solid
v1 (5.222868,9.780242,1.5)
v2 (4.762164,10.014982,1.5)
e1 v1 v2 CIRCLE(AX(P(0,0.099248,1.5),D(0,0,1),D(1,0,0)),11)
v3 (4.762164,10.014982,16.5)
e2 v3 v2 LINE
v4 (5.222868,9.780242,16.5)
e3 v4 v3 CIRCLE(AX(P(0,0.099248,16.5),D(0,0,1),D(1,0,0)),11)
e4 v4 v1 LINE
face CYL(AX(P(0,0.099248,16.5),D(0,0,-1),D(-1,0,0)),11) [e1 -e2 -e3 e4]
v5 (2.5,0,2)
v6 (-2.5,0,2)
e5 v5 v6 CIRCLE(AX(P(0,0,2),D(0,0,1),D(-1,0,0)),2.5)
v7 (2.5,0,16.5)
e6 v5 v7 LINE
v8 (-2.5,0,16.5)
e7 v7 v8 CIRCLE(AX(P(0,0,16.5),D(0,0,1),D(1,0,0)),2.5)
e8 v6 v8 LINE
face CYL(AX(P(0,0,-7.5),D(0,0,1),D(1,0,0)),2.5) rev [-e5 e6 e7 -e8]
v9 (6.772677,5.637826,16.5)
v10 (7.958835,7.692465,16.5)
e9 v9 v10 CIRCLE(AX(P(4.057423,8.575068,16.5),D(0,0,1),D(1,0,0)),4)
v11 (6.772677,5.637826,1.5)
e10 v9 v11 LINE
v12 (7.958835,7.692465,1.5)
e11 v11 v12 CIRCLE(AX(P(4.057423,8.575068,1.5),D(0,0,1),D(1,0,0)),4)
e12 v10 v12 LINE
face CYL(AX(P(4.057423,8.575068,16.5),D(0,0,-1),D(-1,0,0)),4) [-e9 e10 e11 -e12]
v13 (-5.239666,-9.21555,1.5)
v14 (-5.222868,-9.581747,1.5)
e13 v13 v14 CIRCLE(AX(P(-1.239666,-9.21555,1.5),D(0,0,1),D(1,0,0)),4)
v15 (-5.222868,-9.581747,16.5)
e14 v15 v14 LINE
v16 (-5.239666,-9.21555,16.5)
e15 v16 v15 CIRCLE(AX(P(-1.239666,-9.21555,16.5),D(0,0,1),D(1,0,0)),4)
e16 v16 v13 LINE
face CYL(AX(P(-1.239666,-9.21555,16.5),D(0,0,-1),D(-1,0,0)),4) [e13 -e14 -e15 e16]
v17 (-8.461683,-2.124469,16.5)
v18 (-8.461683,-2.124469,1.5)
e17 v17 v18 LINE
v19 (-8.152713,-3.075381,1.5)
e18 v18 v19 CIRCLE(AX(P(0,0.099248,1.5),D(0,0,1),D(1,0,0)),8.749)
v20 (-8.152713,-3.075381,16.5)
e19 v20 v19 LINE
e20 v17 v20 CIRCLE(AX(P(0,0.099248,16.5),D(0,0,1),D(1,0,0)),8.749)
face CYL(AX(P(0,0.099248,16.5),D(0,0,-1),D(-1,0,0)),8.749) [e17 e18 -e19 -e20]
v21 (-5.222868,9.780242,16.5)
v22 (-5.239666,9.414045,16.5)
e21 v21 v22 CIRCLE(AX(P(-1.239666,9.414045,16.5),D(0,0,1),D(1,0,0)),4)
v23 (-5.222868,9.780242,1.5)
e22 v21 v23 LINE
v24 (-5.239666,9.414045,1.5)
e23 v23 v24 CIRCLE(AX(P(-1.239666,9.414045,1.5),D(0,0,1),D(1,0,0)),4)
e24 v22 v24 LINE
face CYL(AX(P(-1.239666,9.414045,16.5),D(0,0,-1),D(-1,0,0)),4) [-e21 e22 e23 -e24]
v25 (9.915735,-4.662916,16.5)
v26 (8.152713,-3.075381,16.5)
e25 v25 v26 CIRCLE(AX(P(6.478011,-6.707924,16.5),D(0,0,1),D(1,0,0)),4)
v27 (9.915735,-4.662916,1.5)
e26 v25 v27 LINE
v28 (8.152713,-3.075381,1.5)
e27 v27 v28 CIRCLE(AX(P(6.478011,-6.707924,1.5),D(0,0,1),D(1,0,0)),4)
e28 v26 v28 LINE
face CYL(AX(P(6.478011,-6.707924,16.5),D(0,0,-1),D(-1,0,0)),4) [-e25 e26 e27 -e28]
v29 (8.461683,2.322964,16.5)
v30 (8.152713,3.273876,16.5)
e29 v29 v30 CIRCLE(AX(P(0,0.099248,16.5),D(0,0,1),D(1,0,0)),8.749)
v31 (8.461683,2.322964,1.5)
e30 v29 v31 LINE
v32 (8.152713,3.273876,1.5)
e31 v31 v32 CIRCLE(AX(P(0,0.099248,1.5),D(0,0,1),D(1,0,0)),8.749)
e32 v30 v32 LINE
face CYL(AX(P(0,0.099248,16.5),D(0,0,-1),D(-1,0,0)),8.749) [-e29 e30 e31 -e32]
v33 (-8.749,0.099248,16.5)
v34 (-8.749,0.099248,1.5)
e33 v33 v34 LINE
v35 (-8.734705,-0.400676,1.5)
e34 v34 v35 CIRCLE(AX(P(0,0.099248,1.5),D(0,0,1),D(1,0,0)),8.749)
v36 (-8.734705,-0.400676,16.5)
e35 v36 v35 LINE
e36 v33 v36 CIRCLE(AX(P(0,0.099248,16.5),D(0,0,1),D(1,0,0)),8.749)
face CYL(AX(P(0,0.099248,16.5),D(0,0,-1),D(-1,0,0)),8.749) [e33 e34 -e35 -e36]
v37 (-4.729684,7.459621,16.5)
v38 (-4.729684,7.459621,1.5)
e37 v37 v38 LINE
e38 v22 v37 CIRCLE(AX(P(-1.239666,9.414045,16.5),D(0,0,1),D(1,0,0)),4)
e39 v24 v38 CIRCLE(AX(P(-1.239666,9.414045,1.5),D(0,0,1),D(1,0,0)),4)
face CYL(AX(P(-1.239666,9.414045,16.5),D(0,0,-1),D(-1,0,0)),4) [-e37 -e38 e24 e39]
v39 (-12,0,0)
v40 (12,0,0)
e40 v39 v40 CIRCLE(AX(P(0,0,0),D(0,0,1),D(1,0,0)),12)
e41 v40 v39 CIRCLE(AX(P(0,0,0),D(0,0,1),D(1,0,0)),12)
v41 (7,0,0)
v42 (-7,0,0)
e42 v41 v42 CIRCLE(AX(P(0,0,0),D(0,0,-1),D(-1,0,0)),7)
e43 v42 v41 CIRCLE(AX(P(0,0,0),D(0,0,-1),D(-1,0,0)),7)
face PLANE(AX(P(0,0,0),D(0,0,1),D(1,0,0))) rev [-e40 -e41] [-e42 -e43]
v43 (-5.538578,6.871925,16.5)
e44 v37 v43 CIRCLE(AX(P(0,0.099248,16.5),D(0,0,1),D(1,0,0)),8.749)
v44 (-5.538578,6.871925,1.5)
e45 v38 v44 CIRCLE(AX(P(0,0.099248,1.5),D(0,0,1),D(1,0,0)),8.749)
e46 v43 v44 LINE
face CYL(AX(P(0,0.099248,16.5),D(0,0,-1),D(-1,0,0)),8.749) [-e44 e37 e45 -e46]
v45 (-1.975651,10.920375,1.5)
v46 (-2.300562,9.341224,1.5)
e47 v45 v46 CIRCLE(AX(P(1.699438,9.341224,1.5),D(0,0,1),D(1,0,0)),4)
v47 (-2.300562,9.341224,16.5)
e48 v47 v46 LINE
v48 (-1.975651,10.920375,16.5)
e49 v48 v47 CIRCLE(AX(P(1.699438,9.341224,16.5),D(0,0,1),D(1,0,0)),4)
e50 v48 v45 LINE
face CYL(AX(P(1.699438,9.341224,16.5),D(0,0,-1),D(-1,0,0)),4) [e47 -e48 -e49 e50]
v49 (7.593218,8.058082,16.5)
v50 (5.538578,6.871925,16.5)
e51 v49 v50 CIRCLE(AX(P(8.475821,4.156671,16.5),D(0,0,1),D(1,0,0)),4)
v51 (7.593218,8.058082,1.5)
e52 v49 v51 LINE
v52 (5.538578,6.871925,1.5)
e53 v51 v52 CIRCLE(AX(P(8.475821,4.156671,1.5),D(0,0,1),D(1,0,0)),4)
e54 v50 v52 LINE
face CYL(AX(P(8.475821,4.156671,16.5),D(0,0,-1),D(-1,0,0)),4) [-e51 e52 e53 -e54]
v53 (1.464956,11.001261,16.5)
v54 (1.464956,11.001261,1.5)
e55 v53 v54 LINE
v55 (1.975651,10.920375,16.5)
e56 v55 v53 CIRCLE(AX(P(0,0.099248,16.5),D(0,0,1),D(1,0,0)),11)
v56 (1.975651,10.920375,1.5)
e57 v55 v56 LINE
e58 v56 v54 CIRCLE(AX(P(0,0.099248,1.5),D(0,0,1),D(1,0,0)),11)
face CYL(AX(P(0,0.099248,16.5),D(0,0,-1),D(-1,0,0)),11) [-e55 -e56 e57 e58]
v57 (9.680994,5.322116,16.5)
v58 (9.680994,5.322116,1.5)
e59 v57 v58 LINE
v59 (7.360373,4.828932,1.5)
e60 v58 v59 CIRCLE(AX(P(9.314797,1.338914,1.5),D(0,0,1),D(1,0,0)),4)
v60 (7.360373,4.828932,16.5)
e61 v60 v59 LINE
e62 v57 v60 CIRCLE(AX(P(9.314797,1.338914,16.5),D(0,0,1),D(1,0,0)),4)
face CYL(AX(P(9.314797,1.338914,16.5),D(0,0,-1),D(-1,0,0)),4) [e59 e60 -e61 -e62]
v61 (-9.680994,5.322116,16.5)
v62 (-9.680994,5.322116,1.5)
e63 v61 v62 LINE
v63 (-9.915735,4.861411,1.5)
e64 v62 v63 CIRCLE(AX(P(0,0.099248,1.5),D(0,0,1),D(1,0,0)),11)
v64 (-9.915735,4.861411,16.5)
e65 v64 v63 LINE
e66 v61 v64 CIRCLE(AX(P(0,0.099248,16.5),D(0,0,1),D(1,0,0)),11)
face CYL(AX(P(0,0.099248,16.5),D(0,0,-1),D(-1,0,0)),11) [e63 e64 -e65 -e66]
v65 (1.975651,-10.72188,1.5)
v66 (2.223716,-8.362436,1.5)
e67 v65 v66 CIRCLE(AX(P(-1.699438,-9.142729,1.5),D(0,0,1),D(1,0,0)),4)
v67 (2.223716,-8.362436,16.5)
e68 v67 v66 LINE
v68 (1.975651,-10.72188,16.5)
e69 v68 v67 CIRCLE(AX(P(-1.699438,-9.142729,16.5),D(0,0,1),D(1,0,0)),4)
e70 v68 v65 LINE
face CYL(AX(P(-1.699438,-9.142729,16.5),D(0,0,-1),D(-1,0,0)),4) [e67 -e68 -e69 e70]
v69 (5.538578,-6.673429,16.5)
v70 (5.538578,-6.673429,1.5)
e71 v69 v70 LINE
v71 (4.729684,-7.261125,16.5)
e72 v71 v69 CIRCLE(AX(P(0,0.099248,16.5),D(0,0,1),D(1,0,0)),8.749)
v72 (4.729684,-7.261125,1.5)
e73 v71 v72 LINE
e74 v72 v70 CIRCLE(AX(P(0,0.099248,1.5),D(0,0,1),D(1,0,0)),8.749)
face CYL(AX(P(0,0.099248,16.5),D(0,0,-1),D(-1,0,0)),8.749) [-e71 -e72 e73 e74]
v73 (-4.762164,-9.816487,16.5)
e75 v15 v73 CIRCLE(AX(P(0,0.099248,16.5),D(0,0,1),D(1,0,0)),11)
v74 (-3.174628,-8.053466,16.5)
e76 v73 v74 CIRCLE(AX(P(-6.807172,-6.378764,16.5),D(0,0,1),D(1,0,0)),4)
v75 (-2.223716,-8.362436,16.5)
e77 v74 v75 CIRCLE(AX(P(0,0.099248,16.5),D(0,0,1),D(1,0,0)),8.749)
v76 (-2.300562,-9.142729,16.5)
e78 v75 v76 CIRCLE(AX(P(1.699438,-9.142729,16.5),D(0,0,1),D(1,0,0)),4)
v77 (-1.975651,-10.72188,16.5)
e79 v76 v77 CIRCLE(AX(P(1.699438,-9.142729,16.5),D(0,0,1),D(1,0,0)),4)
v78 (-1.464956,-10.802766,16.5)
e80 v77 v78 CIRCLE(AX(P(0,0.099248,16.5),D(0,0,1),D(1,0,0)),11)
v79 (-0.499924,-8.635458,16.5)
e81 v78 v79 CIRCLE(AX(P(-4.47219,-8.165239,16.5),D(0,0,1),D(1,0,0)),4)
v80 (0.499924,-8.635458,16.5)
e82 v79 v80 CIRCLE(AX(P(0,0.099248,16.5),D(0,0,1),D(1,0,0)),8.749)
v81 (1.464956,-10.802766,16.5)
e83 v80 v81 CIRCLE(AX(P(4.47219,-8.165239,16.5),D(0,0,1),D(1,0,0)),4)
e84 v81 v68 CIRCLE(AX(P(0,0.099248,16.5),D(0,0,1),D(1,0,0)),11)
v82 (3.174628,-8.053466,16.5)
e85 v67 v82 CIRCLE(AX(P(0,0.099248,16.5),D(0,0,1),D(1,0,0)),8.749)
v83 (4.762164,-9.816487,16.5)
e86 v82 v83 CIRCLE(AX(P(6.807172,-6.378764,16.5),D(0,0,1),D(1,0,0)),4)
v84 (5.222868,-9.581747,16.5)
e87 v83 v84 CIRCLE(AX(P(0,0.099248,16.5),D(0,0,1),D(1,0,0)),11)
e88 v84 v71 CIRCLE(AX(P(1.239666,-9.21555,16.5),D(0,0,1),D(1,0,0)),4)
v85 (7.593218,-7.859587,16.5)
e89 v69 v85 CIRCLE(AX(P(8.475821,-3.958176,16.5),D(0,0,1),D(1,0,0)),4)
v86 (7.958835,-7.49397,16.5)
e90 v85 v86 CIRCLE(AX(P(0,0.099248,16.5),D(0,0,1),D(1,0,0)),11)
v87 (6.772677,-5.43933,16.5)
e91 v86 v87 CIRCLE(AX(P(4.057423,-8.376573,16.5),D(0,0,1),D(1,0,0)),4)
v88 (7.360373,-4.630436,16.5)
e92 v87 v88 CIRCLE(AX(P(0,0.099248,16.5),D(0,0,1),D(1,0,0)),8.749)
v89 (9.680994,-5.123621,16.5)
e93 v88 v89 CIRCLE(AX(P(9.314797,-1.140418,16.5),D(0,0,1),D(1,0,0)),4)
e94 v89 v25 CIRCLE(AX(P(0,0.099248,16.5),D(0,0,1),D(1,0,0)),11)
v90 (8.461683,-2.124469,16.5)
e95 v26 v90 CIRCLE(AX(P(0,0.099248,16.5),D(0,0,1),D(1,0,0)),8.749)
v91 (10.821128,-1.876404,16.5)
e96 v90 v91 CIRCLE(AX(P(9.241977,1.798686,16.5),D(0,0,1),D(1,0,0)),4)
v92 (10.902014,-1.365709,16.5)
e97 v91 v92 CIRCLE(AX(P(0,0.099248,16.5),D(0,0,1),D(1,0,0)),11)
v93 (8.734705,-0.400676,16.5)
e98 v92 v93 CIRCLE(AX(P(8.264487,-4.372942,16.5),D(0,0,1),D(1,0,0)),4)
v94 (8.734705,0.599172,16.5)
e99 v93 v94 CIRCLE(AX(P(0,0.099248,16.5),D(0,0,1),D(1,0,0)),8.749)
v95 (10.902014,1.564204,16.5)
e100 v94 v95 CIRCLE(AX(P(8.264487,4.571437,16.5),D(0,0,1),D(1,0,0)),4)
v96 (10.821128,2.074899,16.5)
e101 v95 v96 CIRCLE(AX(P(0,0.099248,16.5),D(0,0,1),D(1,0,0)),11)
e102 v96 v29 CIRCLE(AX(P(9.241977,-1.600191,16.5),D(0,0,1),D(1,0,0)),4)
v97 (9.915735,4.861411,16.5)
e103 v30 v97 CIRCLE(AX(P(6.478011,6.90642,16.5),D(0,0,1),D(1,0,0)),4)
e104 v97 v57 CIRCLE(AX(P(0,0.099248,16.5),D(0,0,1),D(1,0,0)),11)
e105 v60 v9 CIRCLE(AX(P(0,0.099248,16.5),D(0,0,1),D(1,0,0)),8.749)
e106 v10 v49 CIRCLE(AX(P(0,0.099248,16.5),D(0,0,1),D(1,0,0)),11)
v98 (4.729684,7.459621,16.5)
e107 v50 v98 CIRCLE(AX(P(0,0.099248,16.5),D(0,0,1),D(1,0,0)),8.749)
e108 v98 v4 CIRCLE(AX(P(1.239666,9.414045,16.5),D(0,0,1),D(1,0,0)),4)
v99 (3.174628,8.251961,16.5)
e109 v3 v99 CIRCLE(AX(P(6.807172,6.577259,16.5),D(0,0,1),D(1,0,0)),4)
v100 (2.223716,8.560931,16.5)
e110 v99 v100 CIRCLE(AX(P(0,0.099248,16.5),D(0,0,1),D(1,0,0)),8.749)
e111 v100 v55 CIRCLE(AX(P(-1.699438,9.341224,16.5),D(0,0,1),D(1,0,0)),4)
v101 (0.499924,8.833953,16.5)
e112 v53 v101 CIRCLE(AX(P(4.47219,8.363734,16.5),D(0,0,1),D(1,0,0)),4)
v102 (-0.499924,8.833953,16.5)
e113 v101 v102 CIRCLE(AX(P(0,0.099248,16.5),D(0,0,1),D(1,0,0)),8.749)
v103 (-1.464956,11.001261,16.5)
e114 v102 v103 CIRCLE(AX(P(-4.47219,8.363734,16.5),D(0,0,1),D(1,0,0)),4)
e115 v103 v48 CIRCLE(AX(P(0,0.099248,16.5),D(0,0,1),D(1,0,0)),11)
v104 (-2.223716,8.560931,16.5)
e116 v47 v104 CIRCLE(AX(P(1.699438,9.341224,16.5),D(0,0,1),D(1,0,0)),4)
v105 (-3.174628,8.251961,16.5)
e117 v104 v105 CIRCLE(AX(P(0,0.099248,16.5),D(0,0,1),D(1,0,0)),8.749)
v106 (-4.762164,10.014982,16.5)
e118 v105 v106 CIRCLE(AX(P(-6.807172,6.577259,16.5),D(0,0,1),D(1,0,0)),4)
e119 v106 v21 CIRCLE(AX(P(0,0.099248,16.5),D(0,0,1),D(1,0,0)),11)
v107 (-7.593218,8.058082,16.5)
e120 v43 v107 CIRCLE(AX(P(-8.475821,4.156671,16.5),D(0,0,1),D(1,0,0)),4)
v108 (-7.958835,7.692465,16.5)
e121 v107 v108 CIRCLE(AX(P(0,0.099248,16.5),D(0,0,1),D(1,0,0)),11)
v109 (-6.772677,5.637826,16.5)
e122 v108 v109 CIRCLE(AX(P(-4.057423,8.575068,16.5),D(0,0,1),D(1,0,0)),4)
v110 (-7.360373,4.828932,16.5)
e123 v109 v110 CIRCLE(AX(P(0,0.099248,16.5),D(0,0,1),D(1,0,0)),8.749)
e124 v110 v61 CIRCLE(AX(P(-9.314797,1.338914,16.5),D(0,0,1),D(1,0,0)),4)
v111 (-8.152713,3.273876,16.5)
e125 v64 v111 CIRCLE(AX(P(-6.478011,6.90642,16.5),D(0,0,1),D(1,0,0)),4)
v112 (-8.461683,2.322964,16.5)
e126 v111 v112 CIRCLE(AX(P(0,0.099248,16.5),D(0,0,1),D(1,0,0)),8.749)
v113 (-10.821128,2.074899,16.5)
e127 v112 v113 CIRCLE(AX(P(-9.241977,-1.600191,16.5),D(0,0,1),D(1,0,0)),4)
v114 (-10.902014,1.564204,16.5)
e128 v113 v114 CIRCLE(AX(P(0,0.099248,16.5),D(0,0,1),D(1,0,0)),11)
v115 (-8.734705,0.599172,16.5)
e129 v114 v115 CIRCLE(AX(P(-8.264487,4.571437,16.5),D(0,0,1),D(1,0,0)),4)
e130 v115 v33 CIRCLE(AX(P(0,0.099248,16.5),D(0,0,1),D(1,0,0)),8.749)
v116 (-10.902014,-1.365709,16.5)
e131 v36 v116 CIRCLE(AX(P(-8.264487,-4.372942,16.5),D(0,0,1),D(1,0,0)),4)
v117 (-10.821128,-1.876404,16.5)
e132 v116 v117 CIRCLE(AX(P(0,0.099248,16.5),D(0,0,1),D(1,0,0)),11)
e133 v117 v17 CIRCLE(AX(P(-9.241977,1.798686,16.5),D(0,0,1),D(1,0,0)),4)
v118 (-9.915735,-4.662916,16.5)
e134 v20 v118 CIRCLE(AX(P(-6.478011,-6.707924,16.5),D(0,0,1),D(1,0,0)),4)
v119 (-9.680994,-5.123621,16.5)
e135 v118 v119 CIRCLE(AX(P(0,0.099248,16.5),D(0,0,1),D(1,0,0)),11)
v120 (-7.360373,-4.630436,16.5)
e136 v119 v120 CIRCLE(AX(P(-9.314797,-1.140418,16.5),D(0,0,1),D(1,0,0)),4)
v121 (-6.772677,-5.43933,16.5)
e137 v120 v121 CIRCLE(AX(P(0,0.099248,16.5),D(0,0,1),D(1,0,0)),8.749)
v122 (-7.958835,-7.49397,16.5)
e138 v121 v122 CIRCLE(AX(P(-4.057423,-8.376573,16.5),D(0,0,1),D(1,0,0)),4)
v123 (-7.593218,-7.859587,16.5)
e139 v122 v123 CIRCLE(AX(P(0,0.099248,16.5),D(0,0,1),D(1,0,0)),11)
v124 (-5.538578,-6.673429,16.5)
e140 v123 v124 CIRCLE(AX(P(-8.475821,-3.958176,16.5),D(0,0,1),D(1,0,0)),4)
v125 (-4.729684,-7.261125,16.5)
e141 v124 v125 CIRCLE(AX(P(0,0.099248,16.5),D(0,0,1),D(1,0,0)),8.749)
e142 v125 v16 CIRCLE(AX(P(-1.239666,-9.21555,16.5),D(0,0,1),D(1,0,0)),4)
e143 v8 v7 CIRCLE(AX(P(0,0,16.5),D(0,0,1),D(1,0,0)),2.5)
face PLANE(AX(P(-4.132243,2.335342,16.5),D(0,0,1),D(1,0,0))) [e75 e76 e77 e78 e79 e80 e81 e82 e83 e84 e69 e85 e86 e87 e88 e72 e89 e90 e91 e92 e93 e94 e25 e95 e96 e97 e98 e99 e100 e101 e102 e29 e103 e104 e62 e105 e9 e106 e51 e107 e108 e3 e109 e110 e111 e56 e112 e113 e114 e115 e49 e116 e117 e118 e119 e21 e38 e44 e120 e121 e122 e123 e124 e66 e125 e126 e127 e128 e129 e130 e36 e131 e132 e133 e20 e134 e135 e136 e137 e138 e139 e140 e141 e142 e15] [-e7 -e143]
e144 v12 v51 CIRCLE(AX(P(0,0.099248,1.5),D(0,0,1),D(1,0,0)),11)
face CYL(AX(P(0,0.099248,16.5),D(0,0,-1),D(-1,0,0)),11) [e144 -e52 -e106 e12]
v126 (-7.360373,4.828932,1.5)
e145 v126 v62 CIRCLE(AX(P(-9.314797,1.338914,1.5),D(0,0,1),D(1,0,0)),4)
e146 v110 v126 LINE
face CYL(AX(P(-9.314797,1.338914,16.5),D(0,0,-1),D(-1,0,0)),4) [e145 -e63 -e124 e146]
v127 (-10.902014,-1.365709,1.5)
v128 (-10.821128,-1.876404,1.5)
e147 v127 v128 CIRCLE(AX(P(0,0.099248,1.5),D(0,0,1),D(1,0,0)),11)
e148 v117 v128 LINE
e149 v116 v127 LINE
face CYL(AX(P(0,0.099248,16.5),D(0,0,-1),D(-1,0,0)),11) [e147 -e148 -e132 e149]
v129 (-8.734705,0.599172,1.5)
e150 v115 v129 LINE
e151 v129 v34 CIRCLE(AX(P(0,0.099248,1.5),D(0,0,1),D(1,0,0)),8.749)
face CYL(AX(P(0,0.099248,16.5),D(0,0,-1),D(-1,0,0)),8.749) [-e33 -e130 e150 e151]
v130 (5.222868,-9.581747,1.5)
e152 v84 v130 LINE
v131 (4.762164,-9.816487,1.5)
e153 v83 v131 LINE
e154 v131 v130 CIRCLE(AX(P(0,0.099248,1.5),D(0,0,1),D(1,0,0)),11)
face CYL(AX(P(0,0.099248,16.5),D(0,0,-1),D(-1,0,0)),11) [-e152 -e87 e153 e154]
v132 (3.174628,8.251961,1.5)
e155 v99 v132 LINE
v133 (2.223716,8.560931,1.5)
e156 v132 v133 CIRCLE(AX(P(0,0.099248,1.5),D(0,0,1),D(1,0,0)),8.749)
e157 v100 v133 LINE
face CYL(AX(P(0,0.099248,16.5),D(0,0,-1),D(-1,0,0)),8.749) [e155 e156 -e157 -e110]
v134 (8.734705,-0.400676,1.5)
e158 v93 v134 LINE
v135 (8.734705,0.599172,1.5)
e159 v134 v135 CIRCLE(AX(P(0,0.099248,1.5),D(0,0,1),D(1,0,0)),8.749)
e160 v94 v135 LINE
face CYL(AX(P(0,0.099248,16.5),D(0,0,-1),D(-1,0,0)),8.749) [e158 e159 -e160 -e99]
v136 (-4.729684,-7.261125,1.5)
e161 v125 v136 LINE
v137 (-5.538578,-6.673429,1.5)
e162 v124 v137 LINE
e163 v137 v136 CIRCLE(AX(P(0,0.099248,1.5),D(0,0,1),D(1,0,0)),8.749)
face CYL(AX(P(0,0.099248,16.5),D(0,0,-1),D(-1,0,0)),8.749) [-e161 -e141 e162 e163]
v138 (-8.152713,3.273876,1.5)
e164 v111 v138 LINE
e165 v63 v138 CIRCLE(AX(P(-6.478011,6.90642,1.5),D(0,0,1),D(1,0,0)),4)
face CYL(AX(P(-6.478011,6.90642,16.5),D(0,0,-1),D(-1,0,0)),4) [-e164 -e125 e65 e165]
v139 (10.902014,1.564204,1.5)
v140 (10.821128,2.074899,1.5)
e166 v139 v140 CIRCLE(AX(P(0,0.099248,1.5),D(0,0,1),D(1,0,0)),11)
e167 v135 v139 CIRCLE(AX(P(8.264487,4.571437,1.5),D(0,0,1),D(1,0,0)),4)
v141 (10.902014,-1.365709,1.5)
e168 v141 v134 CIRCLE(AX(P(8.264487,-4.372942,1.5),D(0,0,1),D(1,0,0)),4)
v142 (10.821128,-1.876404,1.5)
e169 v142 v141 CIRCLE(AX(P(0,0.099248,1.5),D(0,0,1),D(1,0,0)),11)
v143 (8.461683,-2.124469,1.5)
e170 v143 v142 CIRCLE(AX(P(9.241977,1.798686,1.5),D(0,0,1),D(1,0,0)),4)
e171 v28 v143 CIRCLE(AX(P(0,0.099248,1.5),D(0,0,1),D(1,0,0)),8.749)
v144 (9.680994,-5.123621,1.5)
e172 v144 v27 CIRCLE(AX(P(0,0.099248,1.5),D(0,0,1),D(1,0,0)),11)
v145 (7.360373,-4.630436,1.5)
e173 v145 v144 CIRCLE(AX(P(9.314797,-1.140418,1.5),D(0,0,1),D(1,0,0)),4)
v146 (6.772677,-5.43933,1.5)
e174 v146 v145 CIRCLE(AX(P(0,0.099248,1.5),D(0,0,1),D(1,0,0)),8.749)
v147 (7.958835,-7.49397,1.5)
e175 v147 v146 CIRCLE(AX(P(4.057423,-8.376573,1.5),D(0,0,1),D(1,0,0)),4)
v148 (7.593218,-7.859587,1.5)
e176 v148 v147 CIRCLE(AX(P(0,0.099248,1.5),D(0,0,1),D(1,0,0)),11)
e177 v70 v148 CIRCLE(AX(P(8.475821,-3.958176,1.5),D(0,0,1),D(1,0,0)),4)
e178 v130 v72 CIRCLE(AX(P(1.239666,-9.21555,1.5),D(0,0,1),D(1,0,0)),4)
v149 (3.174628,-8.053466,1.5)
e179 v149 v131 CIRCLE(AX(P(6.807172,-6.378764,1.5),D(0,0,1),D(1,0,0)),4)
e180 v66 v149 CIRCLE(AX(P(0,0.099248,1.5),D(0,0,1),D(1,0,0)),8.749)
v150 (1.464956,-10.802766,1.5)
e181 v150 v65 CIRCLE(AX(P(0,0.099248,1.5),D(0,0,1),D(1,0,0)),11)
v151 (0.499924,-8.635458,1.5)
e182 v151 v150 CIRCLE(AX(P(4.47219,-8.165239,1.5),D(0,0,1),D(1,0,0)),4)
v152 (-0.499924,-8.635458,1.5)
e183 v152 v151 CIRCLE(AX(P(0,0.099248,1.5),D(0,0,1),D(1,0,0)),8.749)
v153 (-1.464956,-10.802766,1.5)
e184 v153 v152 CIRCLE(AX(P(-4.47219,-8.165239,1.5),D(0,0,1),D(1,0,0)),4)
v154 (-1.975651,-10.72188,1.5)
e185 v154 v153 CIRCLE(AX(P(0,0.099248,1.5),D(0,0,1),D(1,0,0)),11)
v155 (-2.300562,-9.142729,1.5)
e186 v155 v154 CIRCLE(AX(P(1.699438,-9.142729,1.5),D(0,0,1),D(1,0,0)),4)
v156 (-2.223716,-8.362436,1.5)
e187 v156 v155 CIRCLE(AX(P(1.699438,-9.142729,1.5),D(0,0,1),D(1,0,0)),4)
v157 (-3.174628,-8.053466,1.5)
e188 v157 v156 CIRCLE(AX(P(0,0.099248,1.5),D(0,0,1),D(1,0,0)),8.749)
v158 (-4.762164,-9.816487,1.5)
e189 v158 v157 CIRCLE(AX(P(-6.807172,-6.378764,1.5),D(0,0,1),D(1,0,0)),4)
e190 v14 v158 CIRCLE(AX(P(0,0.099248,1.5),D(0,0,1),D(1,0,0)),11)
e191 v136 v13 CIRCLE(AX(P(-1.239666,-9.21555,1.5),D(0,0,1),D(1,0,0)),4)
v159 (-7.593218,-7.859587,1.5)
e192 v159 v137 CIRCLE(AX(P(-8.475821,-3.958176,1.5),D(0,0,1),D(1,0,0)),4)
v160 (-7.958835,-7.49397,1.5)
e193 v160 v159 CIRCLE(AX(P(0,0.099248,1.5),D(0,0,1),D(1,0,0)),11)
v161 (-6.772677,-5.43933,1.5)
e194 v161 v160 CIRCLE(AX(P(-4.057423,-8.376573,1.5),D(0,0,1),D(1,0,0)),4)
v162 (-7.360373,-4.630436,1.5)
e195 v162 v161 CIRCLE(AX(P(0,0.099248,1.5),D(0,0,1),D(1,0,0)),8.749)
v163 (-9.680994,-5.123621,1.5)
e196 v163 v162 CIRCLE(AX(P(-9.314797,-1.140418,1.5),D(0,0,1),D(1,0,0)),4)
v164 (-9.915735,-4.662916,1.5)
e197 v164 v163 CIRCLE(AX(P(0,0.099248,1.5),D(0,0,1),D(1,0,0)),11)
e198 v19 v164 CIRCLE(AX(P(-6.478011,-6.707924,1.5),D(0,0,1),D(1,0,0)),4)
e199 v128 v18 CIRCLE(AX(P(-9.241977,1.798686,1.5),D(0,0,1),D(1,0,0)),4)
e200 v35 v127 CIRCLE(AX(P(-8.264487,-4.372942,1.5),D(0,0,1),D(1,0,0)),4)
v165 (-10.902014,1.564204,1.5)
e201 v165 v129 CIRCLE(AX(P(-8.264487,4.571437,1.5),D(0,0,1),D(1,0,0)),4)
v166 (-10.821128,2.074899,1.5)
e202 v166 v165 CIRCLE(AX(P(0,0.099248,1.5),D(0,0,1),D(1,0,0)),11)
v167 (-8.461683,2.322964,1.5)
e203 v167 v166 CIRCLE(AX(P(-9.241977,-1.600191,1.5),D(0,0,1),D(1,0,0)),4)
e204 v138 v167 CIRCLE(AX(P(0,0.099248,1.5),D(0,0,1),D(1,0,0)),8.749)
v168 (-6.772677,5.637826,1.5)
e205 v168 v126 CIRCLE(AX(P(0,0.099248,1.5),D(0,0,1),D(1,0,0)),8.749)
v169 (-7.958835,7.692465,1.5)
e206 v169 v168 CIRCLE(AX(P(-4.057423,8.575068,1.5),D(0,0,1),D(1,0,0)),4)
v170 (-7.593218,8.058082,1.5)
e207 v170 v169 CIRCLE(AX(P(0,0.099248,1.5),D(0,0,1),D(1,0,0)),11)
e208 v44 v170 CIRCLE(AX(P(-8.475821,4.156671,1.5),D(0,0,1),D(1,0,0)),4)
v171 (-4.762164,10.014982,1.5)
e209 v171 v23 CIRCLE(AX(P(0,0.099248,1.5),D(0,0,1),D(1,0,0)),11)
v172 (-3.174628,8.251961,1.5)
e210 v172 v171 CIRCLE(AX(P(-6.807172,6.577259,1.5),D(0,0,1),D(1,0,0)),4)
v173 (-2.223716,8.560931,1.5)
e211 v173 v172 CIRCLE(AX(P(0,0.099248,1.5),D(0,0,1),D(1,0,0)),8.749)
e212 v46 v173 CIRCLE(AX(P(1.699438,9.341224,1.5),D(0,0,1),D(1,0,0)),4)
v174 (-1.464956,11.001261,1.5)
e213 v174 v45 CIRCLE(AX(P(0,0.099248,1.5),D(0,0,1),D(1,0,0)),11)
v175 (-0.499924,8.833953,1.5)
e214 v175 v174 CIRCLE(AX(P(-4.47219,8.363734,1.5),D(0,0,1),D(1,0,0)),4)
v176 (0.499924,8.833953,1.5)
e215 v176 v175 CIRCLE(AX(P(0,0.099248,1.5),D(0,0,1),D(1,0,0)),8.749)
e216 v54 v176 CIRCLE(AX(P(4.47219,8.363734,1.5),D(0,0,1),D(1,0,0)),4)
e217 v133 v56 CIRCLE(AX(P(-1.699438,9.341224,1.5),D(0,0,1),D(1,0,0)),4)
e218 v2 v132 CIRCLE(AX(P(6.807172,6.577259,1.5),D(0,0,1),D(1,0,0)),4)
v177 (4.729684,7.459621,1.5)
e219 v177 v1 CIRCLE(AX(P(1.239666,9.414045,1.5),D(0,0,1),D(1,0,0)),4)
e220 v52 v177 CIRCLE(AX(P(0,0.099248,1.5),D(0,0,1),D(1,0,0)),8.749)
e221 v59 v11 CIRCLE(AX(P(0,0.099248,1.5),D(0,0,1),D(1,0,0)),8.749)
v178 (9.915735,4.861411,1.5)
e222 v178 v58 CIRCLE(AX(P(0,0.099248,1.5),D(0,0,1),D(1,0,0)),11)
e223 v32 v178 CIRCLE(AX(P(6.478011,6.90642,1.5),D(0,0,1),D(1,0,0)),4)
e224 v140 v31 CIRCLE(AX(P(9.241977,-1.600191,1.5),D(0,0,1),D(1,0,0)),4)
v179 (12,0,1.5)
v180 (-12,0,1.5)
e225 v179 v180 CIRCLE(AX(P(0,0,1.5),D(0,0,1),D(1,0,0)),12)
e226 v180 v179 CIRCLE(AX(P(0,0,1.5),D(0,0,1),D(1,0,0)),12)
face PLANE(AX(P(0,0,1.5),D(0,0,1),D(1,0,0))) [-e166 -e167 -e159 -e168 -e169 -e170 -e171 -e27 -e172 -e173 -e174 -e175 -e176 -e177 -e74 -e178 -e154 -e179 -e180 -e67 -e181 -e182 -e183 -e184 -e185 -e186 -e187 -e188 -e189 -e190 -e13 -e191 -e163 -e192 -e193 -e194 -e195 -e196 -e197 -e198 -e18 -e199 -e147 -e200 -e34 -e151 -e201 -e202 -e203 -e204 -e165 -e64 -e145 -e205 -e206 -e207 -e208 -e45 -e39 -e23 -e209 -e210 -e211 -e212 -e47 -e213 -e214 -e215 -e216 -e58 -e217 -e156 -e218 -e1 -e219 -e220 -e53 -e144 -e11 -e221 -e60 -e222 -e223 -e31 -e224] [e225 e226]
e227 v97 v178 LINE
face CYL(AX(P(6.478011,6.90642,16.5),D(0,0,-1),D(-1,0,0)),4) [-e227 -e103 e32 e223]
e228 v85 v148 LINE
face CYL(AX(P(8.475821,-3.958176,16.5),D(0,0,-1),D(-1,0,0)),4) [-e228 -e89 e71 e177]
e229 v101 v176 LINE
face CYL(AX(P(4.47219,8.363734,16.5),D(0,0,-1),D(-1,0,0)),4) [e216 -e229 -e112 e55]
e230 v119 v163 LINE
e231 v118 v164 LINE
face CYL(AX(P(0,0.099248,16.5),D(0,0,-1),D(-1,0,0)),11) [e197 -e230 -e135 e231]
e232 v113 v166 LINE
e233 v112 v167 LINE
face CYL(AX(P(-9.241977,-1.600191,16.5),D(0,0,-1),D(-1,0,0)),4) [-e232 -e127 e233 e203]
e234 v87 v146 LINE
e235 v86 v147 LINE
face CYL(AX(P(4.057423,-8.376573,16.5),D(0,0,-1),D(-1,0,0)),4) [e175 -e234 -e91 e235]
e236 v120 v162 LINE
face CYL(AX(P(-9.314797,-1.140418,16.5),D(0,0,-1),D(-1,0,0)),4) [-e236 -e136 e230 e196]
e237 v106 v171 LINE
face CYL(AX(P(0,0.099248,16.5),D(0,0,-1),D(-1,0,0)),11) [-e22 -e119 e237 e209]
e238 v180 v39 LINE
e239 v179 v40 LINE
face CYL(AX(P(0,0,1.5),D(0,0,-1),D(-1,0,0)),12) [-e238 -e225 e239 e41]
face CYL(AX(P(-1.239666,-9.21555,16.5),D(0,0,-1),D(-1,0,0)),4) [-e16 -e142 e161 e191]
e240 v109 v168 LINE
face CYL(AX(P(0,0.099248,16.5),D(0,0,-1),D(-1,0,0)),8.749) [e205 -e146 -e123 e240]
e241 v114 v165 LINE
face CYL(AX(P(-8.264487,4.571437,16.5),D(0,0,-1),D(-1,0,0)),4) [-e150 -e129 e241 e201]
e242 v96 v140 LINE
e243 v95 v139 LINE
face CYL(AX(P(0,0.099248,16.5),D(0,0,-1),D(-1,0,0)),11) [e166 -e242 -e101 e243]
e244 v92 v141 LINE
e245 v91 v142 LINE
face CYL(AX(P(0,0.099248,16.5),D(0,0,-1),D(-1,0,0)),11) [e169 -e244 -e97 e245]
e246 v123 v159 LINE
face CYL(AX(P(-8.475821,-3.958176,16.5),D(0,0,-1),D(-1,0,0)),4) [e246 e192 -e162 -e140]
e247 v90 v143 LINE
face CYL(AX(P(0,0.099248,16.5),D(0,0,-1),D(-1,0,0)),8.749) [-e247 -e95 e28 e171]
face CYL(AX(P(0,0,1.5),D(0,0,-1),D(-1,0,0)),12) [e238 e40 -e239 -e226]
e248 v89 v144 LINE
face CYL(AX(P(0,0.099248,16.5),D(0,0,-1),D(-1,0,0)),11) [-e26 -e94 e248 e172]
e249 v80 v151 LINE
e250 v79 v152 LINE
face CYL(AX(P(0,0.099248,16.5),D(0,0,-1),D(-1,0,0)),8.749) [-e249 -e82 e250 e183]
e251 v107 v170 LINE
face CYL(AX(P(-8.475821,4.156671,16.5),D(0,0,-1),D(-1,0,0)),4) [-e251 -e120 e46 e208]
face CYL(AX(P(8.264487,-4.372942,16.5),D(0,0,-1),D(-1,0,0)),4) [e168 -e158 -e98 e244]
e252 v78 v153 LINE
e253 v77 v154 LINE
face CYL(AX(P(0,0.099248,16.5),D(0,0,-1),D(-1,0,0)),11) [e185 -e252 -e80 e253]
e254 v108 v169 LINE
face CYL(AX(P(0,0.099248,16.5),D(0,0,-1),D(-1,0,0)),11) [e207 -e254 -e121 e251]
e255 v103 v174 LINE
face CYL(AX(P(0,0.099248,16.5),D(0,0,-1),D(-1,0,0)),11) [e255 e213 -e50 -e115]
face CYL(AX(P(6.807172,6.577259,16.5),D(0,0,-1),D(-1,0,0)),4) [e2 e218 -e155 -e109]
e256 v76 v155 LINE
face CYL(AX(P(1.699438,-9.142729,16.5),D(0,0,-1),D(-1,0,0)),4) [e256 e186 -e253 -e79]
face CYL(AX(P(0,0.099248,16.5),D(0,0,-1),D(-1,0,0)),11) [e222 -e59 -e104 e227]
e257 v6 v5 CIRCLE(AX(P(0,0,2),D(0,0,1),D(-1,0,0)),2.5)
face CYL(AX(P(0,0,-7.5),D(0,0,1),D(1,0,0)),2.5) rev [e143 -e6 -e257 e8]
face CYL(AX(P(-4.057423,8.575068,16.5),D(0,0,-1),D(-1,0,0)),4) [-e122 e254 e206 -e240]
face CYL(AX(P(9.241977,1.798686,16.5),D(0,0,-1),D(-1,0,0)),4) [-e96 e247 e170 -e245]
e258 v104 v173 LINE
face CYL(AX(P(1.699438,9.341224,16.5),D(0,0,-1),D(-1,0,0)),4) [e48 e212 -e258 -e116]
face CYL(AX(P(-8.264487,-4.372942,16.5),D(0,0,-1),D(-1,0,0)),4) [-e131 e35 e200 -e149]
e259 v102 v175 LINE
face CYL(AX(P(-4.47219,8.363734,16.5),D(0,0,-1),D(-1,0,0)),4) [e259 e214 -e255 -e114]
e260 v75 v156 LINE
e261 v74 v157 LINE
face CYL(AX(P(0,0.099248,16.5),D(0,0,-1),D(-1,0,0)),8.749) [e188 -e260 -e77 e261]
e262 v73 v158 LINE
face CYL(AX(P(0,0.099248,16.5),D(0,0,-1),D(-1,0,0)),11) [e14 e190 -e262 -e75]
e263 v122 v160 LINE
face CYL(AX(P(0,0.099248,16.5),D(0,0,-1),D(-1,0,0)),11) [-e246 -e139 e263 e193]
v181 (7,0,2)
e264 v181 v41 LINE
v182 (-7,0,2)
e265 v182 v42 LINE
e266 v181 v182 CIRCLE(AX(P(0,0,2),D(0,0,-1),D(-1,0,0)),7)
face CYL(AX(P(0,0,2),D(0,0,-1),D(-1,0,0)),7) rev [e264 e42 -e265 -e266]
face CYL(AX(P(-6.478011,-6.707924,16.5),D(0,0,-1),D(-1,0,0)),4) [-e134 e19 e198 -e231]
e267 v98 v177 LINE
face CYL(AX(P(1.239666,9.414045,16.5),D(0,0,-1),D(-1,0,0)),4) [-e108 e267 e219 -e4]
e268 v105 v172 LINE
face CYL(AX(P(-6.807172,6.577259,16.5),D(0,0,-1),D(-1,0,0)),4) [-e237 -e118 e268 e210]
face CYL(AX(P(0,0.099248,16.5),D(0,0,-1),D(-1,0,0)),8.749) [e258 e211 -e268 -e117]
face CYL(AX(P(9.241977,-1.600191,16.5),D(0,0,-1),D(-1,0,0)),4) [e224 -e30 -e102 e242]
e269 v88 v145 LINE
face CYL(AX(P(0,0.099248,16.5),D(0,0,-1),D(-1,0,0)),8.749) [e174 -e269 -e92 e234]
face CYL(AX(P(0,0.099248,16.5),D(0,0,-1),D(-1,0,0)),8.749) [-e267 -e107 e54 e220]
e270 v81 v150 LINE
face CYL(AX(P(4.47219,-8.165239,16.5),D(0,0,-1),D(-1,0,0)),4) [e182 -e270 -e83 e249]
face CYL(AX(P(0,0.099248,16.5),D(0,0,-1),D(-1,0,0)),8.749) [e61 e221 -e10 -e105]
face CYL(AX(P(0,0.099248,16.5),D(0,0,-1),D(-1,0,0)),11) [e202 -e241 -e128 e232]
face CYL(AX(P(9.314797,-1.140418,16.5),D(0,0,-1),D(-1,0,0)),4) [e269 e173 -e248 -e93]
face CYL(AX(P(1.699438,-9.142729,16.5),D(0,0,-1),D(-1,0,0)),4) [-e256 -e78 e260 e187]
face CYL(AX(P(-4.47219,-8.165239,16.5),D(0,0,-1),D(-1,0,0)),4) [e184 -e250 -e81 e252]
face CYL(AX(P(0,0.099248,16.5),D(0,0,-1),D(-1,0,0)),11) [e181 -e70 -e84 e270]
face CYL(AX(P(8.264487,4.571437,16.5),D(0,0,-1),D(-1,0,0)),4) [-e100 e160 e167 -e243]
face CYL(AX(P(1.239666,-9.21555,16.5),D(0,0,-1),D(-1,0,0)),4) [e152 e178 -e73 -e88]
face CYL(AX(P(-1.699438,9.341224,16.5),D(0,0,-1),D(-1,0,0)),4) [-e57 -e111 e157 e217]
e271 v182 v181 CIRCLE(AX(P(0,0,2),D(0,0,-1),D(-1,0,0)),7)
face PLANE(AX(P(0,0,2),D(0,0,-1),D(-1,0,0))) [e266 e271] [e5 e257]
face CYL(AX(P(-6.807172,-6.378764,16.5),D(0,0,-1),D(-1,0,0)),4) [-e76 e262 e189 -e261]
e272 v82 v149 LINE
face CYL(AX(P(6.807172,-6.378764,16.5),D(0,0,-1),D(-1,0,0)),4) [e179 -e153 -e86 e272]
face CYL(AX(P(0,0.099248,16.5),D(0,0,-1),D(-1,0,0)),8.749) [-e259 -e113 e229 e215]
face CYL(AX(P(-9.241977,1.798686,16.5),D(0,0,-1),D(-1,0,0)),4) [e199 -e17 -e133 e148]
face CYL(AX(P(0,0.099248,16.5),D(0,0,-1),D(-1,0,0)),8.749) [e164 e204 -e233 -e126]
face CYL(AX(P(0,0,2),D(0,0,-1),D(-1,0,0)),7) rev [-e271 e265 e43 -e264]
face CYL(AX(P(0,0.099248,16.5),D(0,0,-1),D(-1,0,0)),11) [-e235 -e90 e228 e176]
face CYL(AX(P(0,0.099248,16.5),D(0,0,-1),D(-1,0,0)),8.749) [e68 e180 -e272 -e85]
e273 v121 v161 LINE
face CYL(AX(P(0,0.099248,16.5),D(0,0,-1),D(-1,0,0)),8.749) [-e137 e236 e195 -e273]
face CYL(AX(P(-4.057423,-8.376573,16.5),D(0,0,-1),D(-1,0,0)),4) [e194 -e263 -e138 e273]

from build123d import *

# Parameters (mm, degrees)
SKETCH1_R           = 12
BOSS_EXTRUDE1_DEPTH = 1.5
BOSS_EXTRUDE2_DEPTH = 15
SKETCH3_R           = 2.5
CUT_EXTRUDE1_DEPTH  = 24
SKETCH4_R           = 7
CUT_EXTRUDE2_DEPTH  = 2


with BuildPart() as part:
    # Sketch1 → Boss-Extrude1 (new body)
    with BuildSketch(Plane.XY):
        Circle(SKETCH1_R)
    extrude(amount=BOSS_EXTRUDE1_DEPTH)

    # Sketch2 → Boss-Extrude2 (add)
    with BuildSketch(Plane.XY.offset(1.5)):
        with BuildLine():
            ThreePointArc((-10.902013697, 1.564204022), (-9.891552344, 0.917308412), (-8.734705318, 0.599171595))
            ThreePointArc((-8.734705318, 0.599171595), (-8.749, 0.099247587), (-8.734705318, -0.40067642))
            ThreePointArc((-8.734705318, -0.40067642), (-9.891552344, -0.718813238), (-10.902013697, -1.365708848))
            ThreePointArc((-10.902013697, -1.365708848), (-10.864571747, -1.621531528), (-10.821127601, -1.876403554))
            ThreePointArc((-10.821127601, -1.876403554), (-9.66022001, -2.179388109), (-8.461683425, -2.124468812))
            ThreePointArc((-8.461683425, -2.124468812), (-8.320793461, -2.604342097), (-8.152713396, -3.075380782))
            ThreePointArc((-8.152713396, -3.075380782), (-9.154630615, -3.735432266), (-9.915734733, -4.662916282))
            ThreePointArc((-9.915734733, -4.662916282), (-9.801071766, -4.89464791), (-9.680994141, -5.123620632))
            ThreePointArc((-9.680994141, -5.123620632), (-8.483278035, -5.053035893), (-7.360373002, -4.630436364))
            ThreePointArc((-7.360373002, -4.630436364), (-7.078089684, -5.043285585), (-6.772677084, -5.4393304))
            ThreePointArc((-6.772677084, -5.4393304), (-7.521589858, -6.376686112), (-7.958834566, -7.493969936))
            ThreePointArc((-7.958834566, -7.493969936), (-7.778174593, -7.678927006), (-7.593217523, -7.859586978))
            ThreePointArc((-7.593217523, -7.859586978), (-6.4759337, -7.422342271), (-5.538577987, -6.673429497))
            ThreePointArc((-5.538577987, -6.673429497), (-5.142533172, -6.978842097), (-4.729683951, -7.261125414))
            ThreePointArc((-4.729683951, -7.261125414), (-5.15228348, -8.384030448), (-5.222868219, -9.581746554))
            ThreePointArc((-5.222868219, -9.581746554), (-4.993895497, -9.701824179), (-4.762163869, -9.816487145))
            ThreePointArc((-4.762163869, -9.816487145), (-3.834679853, -9.055383028), (-3.174628369, -8.053465809))
            ThreePointArc((-3.174628369, -8.053465809), (-2.703589684, -8.221545874), (-2.223716399, -8.362435837))
            ThreePointArc((-2.223716399, -8.362435837), (-2.278635697, -9.560972423), (-1.975651141, -10.721880014))
            ThreePointArc((-1.975651141, -10.721880014), (-1.720779115, -10.765324159), (-1.464956435, -10.802766109))
            ThreePointArc((-1.464956435, -10.802766109), (-0.818060825, -9.792304756), (-0.499924007, -8.63545773))
            ThreePointArc((-0.499924007, -8.63545773), (0, -8.649752413), (0.499924007, -8.63545773))
            ThreePointArc((0.499924007, -8.63545773), (0.818060825, -9.792304756), (1.464956435, -10.802766109))
            ThreePointArc((1.464956435, -10.802766109), (1.720779115, -10.765324159), (1.975651141, -10.721880014))
            ThreePointArc((1.975651141, -10.721880014), (2.278635697, -9.560972423), (2.223716399, -8.362435837))
            ThreePointArc((2.223716399, -8.362435837), (2.703589684, -8.221545874), (3.174628369, -8.053465809))
            ThreePointArc((3.174628369, -8.053465809), (3.834679853, -9.055383028), (4.762163869, -9.816487145))
            ThreePointArc((4.762163869, -9.816487145), (4.993895497, -9.701824179), (5.222868219, -9.581746554))
            ThreePointArc((5.222868219, -9.581746554), (5.15228348, -8.384030448), (4.729683951, -7.261125414))
            ThreePointArc((4.729683951, -7.261125414), (5.142533172, -6.978842097), (5.538577987, -6.673429497))
            ThreePointArc((5.538577987, -6.673429497), (6.4759337, -7.422342271), (7.593217523, -7.859586978))
            ThreePointArc((7.593217523, -7.859586978), (7.778174593, -7.678927006), (7.958834566, -7.493969936))
            ThreePointArc((7.958834566, -7.493969936), (7.521589858, -6.376686112), (6.772677084, -5.4393304))
            ThreePointArc((6.772677084, -5.4393304), (7.078089684, -5.043285585), (7.360373002, -4.630436364))
            ThreePointArc((7.360373002, -4.630436364), (8.483278035, -5.053035893), (9.680994141, -5.123620632))
            ThreePointArc((9.680994141, -5.123620632), (9.801071766, -4.89464791), (9.915734733, -4.662916282))
            ThreePointArc((9.915734733, -4.662916282), (9.154630615, -3.735432266), (8.152713396, -3.075380782))
            ThreePointArc((8.152713396, -3.075380782), (8.320793461, -2.604342097), (8.461683425, -2.124468812))
            ThreePointArc((8.461683425, -2.124468812), (9.66022001, -2.179388109), (10.821127601, -1.876403554))
            ThreePointArc((10.821127601, -1.876403554), (10.864571747, -1.621531528), (10.902013697, -1.365708848))
            ThreePointArc((10.902013697, -1.365708848), (9.891552344, -0.718813238), (8.734705318, -0.40067642))
            ThreePointArc((8.734705318, -0.40067642), (8.749, 0.099247587), (8.734705318, 0.599171595))
            ThreePointArc((8.734705318, 0.599171595), (9.891552344, 0.917308412), (10.902013697, 1.564204022))
            ThreePointArc((10.902013697, 1.564204022), (10.864571747, 1.820026703), (10.821127601, 2.074898729))
            ThreePointArc((10.821127601, 2.074898729), (9.66022001, 2.377883284), (8.461683425, 2.322963986))
            ThreePointArc((8.461683425, 2.322963986), (8.320793461, 2.802837271), (8.152713396, 3.273875956))
            ThreePointArc((8.152713396, 3.273875956), (9.154630615, 3.933927441), (9.915734733, 4.861411456))
            ThreePointArc((9.915734733, 4.861411456), (9.801071766, 5.093143084), (9.680994141, 5.322115806))
            ThreePointArc((9.680994141, 5.322115806), (8.483278035, 5.251531067), (7.360373002, 4.828931538))
            ThreePointArc((7.360373002, 4.828931538), (7.078089684, 5.24178076), (6.772677084, 5.637825574))
            ThreePointArc((6.772677084, 5.637825574), (7.521589858, 6.575181287), (7.958834566, 7.692465111))
            ThreePointArc((7.958834566, 7.692465111), (7.778174593, 7.87742218), (7.593217523, 8.058082153))
            ThreePointArc((7.593217523, 8.058082153), (6.4759337, 7.620837446), (5.538577987, 6.871924671))
            ThreePointArc((5.538577987, 6.871924671), (5.142533172, 7.177337271), (4.729683951, 7.459620589))
            ThreePointArc((4.729683951, 7.459620589), (5.15228348, 8.582525623), (5.222868219, 9.780241729))
            ThreePointArc((5.222868219, 9.780241729), (4.993895497, 9.900319353), (4.762163869, 10.01498232))
            ThreePointArc((4.762163869, 10.01498232), (3.834679853, 9.253878203), (3.174628369, 8.251960983))
            ThreePointArc((3.174628369, 8.251960983), (2.703589684, 8.420041048), (2.223716399, 8.560931012))
            ThreePointArc((2.223716399, 8.560931012), (2.278635697, 9.759467597), (1.975651141, 10.920375189))
            ThreePointArc((1.975651141, 10.920375189), (1.720779115, 10.963819334), (1.464956435, 11.001261284))
            ThreePointArc((1.464956435, 11.001261284), (0.818060825, 9.990799931), (0.499924007, 8.833952905))
            ThreePointArc((0.499924007, 8.833952905), (0, 8.848247587), (-0.499924007, 8.833952905))
            ThreePointArc((-0.499924007, 8.833952905), (-0.818060825, 9.990799931), (-1.464956435, 11.001261284))
            ThreePointArc((-1.464956435, 11.001261284), (-1.720779115, 10.963819334), (-1.975651141, 10.920375189))
            ThreePointArc((-1.975651141, 10.920375189), (-2.278635697, 9.759467597), (-2.223716399, 8.560931012))
            ThreePointArc((-2.223716399, 8.560931012), (-2.703589684, 8.420041048), (-3.174628369, 8.251960983))
            ThreePointArc((-3.174628369, 8.251960983), (-3.834679853, 9.253878203), (-4.762163869, 10.01498232))
            ThreePointArc((-4.762163869, 10.01498232), (-4.993895497, 9.900319353), (-5.222868219, 9.780241729))
            ThreePointArc((-5.222868219, 9.780241729), (-5.15228348, 8.582525623), (-4.729683951, 7.459620589))
            ThreePointArc((-4.729683951, 7.459620589), (-5.142533172, 7.177337271), (-5.538577987, 6.871924671))
            ThreePointArc((-5.538577987, 6.871924671), (-6.4759337, 7.620837446), (-7.593217523, 8.058082153))
            ThreePointArc((-7.593217523, 8.058082153), (-7.778174593, 7.87742218), (-7.958834566, 7.692465111))
            ThreePointArc((-7.958834566, 7.692465111), (-7.521589858, 6.575181287), (-6.772677084, 5.637825574))
            ThreePointArc((-6.772677084, 5.637825574), (-7.078089684, 5.24178076), (-7.360373002, 4.828931538))
            ThreePointArc((-7.360373002, 4.828931538), (-8.483278035, 5.251531067), (-9.680994141, 5.322115806))
            ThreePointArc((-9.680994141, 5.322115806), (-9.801071766, 5.093143084), (-9.915734733, 4.861411456))
            ThreePointArc((-9.915734733, 4.861411456), (-9.154630615, 3.933927441), (-8.152713396, 3.273875956))
            ThreePointArc((-8.152713396, 3.273875956), (-8.320793461, 2.802837271), (-8.461683425, 2.322963986))
            ThreePointArc((-8.461683425, 2.322963986), (-9.66022001, 2.377883284), (-10.821127601, 2.074898729))
            ThreePointArc((-10.821127601, 2.074898729), (-10.864571747, 1.820026703), (-10.902013697, 1.564204022))
        make_face()
    extrude(amount=BOSS_EXTRUDE2_DEPTH)

    # Sketch3 → Cut-Extrude1 (cut)
    with BuildSketch(Plane.XY.offset(16.5)):
        Circle(SKETCH3_R)
    extrude(amount=-CUT_EXTRUDE1_DEPTH, mode=Mode.SUBTRACT)

    # Sketch4 → Cut-Extrude2 (cut)
    with BuildSketch(Plane(origin=(0, 0, 0), x_dir=(-1, 0, 0), z_dir=(0, 0, -1))):
        Circle(SKETCH4_R)
    extrude(amount=-CUT_EXTRUDE2_DEPTH, mode=Mode.SUBTRACT)


solid = part.part
